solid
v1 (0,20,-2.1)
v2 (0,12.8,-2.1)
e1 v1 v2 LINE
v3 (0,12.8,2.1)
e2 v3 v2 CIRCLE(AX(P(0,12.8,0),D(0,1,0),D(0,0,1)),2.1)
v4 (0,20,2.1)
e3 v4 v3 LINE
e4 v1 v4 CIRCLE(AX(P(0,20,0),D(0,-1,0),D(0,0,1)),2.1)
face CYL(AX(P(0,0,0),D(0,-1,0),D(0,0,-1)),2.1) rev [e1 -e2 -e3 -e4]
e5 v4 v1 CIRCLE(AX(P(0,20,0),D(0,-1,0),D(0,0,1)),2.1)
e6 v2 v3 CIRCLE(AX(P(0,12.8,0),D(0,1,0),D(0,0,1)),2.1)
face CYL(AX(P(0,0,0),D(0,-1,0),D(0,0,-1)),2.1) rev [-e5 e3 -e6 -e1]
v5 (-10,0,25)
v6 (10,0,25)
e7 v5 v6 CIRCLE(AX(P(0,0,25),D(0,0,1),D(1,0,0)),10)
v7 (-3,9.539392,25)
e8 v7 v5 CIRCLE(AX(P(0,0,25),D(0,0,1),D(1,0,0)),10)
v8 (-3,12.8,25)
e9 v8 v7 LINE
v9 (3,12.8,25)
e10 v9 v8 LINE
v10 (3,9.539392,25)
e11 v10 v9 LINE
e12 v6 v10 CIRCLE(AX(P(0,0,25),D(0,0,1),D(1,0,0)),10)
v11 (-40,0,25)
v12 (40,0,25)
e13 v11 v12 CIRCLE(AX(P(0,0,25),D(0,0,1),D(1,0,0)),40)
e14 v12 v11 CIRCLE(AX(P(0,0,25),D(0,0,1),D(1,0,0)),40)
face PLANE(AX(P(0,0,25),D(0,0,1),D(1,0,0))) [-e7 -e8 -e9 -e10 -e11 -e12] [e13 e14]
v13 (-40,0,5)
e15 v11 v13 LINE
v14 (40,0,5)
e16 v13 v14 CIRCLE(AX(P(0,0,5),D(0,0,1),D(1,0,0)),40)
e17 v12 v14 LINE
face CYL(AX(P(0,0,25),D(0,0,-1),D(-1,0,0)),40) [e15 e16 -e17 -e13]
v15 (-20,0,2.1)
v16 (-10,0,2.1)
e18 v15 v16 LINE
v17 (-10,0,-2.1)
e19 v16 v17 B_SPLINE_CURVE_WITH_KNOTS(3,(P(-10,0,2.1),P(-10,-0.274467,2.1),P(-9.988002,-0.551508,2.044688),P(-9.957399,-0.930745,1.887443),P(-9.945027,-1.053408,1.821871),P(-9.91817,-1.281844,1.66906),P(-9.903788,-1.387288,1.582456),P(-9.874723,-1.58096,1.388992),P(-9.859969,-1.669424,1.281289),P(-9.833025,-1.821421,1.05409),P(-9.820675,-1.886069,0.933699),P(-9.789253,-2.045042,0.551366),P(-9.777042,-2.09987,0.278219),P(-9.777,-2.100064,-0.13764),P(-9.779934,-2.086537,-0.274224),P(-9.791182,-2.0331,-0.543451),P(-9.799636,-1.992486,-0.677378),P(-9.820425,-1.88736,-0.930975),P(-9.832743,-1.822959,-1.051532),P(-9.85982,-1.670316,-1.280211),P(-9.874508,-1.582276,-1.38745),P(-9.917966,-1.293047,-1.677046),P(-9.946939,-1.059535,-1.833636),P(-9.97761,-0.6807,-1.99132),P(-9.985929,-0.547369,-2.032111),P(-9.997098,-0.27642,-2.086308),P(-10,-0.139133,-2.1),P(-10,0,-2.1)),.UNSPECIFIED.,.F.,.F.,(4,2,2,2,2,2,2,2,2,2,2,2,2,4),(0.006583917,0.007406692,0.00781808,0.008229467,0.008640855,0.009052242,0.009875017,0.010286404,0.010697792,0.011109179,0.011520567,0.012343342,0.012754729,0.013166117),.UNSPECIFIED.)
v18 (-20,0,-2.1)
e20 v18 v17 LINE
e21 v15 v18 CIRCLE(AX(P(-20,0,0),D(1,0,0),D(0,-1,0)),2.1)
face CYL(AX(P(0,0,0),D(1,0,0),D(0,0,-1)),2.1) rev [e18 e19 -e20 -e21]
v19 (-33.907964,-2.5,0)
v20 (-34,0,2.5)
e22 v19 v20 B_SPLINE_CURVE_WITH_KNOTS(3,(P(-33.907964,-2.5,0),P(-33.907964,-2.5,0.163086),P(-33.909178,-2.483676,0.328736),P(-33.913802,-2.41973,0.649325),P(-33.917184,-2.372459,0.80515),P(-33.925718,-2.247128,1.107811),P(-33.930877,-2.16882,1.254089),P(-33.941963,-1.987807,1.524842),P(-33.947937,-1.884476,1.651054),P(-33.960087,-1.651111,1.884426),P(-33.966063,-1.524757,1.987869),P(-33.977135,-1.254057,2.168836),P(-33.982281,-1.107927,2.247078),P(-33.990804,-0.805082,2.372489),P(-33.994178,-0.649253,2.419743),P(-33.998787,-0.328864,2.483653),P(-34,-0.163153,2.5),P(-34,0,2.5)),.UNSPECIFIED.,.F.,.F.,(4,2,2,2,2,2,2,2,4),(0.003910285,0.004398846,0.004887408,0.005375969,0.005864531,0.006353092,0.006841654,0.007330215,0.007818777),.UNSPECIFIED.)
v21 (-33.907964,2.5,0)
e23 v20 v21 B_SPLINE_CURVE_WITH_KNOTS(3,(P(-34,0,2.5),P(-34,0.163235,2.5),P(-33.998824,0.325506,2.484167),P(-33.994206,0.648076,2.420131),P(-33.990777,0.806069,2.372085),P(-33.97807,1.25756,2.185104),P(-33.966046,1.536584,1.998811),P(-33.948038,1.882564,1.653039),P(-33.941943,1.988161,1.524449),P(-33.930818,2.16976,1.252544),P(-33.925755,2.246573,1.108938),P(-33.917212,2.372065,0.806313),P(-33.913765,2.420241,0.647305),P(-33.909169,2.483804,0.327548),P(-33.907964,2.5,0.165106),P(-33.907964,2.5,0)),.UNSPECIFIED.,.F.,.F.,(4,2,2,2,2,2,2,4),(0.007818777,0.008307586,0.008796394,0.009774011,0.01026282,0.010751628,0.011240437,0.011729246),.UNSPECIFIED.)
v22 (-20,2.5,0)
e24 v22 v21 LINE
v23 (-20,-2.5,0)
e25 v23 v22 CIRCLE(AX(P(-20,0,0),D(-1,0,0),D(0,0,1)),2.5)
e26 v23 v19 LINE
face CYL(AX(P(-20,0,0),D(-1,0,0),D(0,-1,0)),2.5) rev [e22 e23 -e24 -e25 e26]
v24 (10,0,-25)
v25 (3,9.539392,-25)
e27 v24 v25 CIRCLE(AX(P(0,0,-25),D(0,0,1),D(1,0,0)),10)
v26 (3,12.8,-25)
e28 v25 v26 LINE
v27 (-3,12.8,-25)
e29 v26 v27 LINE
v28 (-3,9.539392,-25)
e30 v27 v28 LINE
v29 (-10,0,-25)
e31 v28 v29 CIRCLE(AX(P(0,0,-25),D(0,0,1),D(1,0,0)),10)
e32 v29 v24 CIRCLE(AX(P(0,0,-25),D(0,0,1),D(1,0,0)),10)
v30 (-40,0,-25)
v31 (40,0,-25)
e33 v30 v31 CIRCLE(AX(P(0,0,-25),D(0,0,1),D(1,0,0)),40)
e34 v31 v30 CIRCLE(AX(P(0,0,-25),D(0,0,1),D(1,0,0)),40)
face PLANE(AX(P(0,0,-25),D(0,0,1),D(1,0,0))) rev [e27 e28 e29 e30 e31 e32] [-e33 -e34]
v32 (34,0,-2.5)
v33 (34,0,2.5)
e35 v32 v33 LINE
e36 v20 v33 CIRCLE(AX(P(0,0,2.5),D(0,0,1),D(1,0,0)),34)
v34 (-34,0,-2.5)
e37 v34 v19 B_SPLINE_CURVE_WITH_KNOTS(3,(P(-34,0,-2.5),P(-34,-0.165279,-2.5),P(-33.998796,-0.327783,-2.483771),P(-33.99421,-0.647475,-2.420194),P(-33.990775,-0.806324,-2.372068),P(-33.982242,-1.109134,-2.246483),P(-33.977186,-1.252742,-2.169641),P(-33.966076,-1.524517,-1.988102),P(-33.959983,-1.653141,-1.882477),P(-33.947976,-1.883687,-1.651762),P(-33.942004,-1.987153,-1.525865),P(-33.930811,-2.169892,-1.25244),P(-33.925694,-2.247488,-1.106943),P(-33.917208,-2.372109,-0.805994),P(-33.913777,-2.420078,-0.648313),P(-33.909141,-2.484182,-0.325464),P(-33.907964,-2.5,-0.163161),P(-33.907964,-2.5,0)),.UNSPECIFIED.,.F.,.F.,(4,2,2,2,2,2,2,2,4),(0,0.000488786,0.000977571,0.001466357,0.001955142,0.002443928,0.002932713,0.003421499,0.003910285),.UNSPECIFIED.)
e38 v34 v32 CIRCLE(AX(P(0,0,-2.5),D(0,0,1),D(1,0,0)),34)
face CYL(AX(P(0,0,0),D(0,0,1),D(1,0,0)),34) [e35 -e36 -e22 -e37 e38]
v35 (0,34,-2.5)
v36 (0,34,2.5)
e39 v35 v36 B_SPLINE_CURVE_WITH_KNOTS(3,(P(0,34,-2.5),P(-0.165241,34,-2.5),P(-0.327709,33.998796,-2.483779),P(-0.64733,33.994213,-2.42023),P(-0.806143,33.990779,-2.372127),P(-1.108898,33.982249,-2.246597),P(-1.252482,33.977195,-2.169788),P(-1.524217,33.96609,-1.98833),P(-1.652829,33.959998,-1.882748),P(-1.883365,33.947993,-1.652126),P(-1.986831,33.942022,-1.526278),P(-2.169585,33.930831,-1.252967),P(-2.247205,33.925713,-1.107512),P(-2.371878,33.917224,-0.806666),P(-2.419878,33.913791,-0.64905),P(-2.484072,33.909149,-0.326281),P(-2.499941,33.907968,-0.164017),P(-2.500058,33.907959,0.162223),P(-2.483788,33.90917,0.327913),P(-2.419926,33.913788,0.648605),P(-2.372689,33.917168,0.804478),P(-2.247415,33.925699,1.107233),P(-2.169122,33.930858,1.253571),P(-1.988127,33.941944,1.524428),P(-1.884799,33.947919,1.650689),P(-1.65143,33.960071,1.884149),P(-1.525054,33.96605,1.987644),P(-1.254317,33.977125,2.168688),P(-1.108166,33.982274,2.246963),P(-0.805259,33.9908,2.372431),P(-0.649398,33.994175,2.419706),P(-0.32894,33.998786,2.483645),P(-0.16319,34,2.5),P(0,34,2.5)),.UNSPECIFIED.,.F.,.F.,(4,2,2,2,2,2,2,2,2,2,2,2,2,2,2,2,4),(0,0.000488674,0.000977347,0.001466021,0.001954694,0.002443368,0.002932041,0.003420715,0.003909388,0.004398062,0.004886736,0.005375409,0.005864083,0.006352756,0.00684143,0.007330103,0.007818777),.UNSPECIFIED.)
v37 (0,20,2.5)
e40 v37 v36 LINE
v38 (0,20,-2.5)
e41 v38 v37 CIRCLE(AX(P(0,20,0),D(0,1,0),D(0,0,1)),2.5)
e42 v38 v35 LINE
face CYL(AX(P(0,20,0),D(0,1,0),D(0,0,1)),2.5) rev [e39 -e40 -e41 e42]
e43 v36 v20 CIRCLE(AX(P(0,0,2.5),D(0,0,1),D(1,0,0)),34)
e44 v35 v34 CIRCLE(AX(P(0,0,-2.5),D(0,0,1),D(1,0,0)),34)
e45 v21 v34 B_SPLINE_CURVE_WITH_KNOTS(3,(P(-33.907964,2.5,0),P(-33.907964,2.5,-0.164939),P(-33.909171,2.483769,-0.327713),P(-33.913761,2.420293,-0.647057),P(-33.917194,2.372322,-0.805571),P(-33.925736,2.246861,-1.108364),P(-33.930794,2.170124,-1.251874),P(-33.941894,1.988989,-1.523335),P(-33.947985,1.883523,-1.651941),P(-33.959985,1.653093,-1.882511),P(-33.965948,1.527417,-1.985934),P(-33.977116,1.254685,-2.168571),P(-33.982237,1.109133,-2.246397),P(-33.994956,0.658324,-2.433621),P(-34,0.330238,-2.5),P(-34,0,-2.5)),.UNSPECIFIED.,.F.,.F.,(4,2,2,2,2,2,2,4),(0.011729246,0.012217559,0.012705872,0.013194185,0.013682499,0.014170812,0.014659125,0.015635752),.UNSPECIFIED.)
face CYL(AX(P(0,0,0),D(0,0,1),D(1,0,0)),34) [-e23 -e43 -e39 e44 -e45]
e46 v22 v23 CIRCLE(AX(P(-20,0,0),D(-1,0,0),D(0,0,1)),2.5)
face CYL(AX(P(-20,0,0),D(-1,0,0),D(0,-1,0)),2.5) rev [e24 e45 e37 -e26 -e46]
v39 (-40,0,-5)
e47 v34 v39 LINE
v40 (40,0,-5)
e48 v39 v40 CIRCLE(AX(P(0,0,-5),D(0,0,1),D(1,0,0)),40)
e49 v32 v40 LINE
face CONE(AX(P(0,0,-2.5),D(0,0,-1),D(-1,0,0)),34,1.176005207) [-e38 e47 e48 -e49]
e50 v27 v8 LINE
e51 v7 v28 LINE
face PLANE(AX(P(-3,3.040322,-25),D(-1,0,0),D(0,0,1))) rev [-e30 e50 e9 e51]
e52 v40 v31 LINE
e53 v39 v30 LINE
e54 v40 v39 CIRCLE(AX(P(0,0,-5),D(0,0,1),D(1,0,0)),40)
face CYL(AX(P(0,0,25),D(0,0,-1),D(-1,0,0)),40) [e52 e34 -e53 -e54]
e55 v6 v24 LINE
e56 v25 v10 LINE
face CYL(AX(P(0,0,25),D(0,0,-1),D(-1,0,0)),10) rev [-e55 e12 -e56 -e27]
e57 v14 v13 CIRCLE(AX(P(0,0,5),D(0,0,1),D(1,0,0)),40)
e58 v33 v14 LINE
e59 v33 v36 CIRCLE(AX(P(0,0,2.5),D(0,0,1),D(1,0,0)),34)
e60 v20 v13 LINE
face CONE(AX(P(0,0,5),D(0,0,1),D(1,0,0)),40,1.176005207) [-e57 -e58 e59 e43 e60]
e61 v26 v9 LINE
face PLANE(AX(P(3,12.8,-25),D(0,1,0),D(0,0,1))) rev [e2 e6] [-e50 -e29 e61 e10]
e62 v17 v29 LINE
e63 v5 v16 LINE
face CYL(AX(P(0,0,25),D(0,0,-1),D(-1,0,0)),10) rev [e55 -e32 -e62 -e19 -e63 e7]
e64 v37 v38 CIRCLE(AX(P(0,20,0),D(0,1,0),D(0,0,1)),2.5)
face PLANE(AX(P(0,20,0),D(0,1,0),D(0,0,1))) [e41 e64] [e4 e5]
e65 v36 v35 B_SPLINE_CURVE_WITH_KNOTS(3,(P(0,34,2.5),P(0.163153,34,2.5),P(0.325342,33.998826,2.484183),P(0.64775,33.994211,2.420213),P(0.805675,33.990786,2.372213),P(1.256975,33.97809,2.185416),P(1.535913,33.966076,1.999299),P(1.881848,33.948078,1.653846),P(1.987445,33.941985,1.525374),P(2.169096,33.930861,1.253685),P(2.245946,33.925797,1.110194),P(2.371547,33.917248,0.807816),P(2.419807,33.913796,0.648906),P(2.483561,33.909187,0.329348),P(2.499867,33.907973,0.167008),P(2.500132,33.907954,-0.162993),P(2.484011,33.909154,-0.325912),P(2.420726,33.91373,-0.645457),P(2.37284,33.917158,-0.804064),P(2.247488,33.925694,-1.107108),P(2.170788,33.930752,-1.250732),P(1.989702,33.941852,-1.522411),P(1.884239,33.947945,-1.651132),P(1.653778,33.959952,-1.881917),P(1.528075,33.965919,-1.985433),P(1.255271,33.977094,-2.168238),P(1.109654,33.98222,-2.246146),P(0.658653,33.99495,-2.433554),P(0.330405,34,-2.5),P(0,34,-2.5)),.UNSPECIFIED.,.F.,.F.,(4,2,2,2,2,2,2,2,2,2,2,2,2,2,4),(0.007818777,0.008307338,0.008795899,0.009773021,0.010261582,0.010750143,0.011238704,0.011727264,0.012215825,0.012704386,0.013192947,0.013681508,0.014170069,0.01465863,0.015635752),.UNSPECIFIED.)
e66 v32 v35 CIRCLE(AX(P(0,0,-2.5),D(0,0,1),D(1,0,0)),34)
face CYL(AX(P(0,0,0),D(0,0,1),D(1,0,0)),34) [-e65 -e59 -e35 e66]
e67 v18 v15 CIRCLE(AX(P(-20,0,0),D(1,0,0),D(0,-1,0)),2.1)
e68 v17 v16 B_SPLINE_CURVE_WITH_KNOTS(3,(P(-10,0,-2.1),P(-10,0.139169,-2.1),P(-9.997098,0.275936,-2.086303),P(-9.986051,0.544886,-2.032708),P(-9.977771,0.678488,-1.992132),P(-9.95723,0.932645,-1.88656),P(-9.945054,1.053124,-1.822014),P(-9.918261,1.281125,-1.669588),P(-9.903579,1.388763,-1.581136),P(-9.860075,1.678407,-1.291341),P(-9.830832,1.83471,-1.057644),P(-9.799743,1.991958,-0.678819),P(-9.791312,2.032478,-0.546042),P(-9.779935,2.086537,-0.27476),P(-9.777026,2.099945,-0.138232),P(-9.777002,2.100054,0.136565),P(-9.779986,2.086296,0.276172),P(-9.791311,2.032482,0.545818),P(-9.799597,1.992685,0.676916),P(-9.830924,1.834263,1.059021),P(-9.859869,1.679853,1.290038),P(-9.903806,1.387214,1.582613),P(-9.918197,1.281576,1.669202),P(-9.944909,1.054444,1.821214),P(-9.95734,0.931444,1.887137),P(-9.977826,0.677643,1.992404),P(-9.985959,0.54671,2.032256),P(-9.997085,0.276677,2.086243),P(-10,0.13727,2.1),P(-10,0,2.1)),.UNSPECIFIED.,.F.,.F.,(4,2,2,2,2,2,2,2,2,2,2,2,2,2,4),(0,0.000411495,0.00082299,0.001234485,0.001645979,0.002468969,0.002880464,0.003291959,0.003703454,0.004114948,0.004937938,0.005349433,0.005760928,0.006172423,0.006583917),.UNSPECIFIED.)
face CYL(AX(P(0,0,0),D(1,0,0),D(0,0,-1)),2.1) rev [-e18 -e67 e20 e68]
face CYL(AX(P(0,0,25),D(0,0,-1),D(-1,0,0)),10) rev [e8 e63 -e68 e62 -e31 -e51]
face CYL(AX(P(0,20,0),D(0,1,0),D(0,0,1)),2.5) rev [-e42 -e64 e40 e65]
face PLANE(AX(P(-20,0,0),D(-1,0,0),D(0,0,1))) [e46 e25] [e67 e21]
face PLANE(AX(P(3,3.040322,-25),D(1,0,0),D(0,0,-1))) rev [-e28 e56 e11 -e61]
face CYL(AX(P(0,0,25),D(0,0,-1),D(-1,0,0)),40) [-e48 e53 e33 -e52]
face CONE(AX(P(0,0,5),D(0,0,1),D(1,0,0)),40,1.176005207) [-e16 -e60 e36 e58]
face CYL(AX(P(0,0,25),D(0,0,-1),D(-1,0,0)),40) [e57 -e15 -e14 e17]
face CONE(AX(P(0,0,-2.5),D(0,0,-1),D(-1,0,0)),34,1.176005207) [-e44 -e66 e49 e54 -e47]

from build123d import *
from build123d.topology import SkipClean

# Parameters (mm, degrees)
SKETCH_1_R               = 40
SKETCH_1_R_2             = 10
EXTRUDE_1_DEPTH          = 25
SKETCH_6_W               = 6
SKETCH_6_H               = 9.759677648
CUT_EXTRUDE_1_DEPTH      = 76.498344353
SKETCH_8_W               = 2.1
SKETCH_8_H               = 40
CUT_EXTRUDE_START        = 40
SKETCH_9_R               = 2.5
CUT_EXTRUDE_2_DEPTH      = 20
PATTERN_CIRCULAR_1_COUNT = 2
PATTERN_CIRCULAR_1_ANGLE = 90


with BuildPart() as part:
    # 草图1 → 凸台-拉伸1 (new, symmetric)
    with BuildSketch(Plane.XY):
        Circle(SKETCH_1_R)
        Circle(SKETCH_1_R_2, mode=Mode.SUBTRACT)
    extrude(amount=EXTRUDE_1_DEPTH, both=True)

    # 草图5 → 切除-旋转1 (revolve, cut)
    with BuildSketch(Plane(origin=(0, 0, 0), x_dir=(1, 0, 0), z_dir=(0, 1, 0)), mode=Mode.PRIVATE) as cut_revolve_1_sk:
        Polygon((-40, -5), (-40, 5), (-34, 2.5), (-34, -2.5), align=None)
    revolve(cut_revolve_1_sk.sketch.rotate(Axis((0, 0, 0), (0, 0, -1)), 180), axis=Axis((0, 0, 0), (0, 0, -1)), mode=Mode.SUBTRACT)

    # 草图6 → 切除-拉伸1 (cut, through all)
    with BuildSketch(Plane.XY.offset(25)):
        with Locations((0, 7.920161176)):
            Rectangle(SKETCH_6_W, SKETCH_6_H)
    extrude(amount=-CUT_EXTRUDE_1_DEPTH, mode=Mode.SUBTRACT)

    # 草图8 → M5 螺纹孔1 (revolve, cut)
    with BuildSketch(Plane(origin=(0, 0, 0), x_dir=(0, 0, -1), z_dir=(1, 0, 0))):
        with Locations((1.05, 20)):
            Rectangle(SKETCH_8_W, SKETCH_8_H)
    hole_wizard_m5_1 = revolve(axis=Axis((0, -6.35, 0), (0, 1, 0)), mode=Mode.SUBTRACT)

    # 草图9 → 切除-拉伸2 (cut)
    with SkipClean():  # the faces are left unmerged after this step: merging them gives an invalid solid
        with BuildSketch(Plane(origin=(0, 0, 0), x_dir=(1, 0, 0), z_dir=(0, 1, 0)).offset(CUT_EXTRUDE_START)):
            with Locations(Location((0, 0, 0), (0, 0, 270))):
                Circle(SKETCH_9_R)
        cut_extrude_2 = extrude(amount=-CUT_EXTRUDE_2_DEPTH, mode=Mode.SUBTRACT)

    # 阵列(圆周)1: M5 螺纹孔1, 切除-拉伸2 ×2 about axis
    pattern_circular_1_axis = Axis((0, 0, 25), (0, 0, 1))
    add([hole_wizard_m5_1.rotate(pattern_circular_1_axis, i * PATTERN_CIRCULAR_1_ANGLE / (PATTERN_CIRCULAR_1_COUNT - 1)) for i in range(1, PATTERN_CIRCULAR_1_COUNT)], mode=Mode.SUBTRACT)
    add([cut_extrude_2.rotate(pattern_circular_1_axis, i * PATTERN_CIRCULAR_1_ANGLE / (PATTERN_CIRCULAR_1_COUNT - 1)) for i in range(1, PATTERN_CIRCULAR_1_COUNT)], mode=Mode.SUBTRACT)


solid = part.part
